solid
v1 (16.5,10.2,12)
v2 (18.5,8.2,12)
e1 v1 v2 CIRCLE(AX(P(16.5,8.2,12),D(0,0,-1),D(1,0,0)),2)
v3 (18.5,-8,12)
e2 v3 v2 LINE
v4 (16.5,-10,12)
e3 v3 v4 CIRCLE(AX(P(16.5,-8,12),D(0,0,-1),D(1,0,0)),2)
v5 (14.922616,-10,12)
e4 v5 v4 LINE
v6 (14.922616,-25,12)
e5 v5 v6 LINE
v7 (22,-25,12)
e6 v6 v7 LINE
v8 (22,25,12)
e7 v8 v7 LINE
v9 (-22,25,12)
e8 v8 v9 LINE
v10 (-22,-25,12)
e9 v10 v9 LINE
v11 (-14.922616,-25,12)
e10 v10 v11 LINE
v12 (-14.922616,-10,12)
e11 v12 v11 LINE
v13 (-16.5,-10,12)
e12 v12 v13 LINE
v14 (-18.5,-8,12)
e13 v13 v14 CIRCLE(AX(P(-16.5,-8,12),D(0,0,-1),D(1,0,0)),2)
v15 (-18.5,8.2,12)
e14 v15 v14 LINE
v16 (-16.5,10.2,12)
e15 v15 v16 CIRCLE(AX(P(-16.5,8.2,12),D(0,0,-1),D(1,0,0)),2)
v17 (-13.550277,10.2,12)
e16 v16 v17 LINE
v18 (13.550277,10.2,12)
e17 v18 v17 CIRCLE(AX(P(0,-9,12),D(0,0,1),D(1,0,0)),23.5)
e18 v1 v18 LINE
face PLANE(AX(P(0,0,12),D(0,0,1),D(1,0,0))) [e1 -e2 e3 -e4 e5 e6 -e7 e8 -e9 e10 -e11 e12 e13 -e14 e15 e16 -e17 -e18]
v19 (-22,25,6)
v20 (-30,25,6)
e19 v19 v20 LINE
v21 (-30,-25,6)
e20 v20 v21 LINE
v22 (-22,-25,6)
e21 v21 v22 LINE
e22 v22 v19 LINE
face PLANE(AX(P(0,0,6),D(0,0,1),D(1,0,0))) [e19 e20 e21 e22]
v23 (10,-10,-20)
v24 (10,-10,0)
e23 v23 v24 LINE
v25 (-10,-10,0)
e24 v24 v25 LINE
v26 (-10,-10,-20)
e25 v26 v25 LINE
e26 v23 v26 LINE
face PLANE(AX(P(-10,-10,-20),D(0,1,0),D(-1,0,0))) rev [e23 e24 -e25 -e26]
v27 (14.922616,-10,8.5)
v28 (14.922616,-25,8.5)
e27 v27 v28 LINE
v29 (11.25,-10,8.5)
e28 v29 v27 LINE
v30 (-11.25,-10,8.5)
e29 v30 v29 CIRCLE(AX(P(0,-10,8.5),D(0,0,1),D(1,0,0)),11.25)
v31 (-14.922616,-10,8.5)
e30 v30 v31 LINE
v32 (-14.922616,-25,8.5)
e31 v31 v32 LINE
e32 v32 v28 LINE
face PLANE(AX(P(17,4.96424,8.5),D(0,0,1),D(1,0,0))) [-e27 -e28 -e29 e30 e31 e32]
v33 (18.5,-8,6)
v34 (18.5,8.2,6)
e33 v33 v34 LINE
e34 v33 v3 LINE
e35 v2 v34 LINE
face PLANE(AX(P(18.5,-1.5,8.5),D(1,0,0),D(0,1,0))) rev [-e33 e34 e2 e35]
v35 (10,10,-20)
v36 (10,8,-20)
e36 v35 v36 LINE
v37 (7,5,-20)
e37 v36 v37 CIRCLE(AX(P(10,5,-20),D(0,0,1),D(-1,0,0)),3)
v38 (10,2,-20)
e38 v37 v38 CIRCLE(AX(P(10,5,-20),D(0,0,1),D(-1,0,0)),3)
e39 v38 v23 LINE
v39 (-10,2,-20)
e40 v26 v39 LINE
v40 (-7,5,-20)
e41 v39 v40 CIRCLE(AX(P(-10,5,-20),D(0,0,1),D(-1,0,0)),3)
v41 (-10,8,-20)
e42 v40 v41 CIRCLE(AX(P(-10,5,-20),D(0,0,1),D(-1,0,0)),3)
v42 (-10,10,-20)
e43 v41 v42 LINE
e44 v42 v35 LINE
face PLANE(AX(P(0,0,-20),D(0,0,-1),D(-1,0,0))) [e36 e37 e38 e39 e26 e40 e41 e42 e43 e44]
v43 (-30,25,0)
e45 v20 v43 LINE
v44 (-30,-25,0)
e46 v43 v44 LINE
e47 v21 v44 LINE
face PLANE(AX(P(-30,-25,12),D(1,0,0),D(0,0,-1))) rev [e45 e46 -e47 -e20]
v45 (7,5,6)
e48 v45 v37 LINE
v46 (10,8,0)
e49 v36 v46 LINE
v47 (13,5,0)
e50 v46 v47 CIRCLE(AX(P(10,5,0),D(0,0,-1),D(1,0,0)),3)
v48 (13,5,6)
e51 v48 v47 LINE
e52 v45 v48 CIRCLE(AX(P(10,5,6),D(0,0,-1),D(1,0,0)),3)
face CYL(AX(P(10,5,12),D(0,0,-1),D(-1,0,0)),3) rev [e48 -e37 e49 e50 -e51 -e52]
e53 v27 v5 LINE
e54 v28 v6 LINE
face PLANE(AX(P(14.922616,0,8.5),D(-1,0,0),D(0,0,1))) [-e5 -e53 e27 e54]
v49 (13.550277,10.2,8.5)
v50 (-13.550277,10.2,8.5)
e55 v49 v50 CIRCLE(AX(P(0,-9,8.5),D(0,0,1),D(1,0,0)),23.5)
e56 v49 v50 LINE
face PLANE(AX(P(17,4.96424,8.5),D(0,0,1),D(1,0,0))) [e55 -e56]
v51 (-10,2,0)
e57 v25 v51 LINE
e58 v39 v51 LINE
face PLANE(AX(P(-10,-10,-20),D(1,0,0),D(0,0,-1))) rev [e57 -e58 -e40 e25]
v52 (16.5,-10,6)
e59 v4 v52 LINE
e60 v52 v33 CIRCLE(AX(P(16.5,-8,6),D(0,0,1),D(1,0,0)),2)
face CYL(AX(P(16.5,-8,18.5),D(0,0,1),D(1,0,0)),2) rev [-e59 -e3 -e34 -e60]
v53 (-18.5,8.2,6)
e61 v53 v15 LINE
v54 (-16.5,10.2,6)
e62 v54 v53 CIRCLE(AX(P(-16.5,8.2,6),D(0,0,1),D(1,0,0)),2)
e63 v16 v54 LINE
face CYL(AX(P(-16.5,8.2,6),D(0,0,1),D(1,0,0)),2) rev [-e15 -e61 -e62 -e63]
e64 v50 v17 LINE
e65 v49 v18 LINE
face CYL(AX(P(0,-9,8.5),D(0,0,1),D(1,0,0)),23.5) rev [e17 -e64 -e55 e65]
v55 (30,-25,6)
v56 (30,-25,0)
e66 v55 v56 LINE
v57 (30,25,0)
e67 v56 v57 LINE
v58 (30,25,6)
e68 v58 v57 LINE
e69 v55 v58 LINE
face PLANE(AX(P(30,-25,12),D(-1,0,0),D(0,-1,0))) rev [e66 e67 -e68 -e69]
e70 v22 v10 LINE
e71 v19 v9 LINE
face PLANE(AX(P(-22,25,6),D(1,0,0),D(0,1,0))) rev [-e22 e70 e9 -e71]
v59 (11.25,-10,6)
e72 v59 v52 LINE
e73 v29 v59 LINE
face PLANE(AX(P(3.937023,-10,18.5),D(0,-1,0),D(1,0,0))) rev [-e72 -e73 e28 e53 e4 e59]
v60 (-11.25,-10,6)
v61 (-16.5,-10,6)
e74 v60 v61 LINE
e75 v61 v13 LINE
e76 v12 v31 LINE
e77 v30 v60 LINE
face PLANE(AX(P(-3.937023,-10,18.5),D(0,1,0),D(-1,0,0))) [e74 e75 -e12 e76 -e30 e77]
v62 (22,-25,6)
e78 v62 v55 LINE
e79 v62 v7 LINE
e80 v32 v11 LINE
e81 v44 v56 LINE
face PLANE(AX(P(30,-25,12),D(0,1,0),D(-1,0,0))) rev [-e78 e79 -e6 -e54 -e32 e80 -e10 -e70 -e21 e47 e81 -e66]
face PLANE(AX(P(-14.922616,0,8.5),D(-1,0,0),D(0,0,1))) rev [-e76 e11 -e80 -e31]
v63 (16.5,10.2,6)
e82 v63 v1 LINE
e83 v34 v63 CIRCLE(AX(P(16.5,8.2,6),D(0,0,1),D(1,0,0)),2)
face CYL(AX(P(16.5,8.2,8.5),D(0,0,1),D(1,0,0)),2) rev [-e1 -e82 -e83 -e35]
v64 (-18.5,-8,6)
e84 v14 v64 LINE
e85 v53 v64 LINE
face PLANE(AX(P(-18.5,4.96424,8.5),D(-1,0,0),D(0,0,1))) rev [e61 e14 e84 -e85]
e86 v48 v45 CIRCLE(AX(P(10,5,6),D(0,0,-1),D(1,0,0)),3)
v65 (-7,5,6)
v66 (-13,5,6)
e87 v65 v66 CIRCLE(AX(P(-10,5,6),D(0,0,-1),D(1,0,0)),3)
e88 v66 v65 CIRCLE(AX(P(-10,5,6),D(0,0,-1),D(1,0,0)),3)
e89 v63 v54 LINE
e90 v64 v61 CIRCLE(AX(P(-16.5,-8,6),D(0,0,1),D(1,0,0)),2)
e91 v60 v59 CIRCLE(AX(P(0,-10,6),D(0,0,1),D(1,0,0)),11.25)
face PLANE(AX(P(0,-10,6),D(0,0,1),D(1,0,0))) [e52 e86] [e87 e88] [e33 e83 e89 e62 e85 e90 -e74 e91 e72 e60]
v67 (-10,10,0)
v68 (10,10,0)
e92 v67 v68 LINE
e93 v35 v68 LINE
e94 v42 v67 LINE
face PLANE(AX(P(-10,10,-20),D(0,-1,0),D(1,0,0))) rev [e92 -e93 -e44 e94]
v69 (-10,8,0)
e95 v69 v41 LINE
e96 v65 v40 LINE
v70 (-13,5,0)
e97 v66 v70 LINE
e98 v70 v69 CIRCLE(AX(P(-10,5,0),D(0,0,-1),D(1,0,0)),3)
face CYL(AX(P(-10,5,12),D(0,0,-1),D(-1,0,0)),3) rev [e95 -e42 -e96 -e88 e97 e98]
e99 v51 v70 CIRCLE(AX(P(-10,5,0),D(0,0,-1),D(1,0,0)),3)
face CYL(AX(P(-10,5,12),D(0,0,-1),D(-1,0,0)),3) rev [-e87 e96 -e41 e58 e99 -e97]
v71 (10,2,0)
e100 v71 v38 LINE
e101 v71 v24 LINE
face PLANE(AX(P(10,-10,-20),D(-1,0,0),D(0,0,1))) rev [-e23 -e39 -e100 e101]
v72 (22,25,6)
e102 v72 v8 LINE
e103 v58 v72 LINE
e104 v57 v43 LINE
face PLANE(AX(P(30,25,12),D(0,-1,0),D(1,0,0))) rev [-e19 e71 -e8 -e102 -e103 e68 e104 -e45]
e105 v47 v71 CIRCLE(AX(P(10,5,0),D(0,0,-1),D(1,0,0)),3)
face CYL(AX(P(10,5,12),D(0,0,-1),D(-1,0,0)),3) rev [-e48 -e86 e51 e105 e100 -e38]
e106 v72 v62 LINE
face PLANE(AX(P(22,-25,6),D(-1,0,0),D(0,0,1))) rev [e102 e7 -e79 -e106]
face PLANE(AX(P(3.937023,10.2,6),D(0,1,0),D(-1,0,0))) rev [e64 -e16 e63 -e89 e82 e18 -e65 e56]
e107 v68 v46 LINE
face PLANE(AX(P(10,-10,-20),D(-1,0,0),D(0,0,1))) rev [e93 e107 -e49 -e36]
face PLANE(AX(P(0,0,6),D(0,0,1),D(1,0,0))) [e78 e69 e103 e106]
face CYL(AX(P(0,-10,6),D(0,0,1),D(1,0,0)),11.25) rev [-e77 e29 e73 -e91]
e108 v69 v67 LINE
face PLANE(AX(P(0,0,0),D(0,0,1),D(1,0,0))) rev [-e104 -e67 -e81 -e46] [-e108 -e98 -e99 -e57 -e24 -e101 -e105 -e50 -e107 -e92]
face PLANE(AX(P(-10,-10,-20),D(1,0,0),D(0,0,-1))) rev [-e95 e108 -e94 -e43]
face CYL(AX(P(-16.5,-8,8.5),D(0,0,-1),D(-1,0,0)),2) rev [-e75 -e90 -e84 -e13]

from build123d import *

# Parameters (mm, degrees)
SKETCH_1_W                      = 60
SKETCH_1_H                      = 50
EXTRUDE_1_DEPTH                 = 12
SKETCH_2_W                      = 20
SKETCH_2_H                      = 20
EXTRUDE_2_DEPTH                 = 20
SKETCH_3_R                      = 10.5
CUT_EXTRUDE_1_DEPTH             = 6
CUT_EXTRUDE_2_DEPTH             = 3.5
CUT_EXTRUDE_3_DEPTH             = 3.5
CUT_EXTRUDE_4_DEPTH             = 2.5
CUT_EXTRUDE_5_REACH             = 48.915
SKETCH_8_R                      = 3
CUT_EXTRUDE_5_DIRECTION_2_DEPTH = 47.914816423
SKETCH_9_W                      = 8
SKETCH_9_H                      = 50
CUT_EXTRUDE_6_DEPTH             = 6
CUT_EXTRUDE_START               = -2.5
SKETCH_10_W                     = 14.56297708
SKETCH_10_H                     = 20.2
CUT_EXTRUDE_7_DEPTH             = 12.5
FILLET_1_R                      = 2


with BuildPart() as part:
    # 草图1 → 凸台-拉伸1 (new body)
    with BuildSketch(Plane.XY):
        Rectangle(SKETCH_1_W, SKETCH_1_H)
    extrude(amount=EXTRUDE_1_DEPTH)

    # 草图2 → 凸台-拉伸2 (add)
    with BuildSketch(Plane(origin=(0, 0, 0), x_dir=(-1, 0, 0), z_dir=(0, 0, -1))):
        Rectangle(SKETCH_2_W, SKETCH_2_H)
    extrude(amount=EXTRUDE_2_DEPTH)

    # 草图3 → 切除-拉伸1 (cut)
    with BuildSketch(Plane.XY.offset(12)):
        with Locations((0, -10)):
            Circle(SKETCH_3_R)
    extrude(amount=-CUT_EXTRUDE_1_DEPTH, mode=Mode.SUBTRACT)

    # 草图5 → 切除-拉伸2 (cut)
    with BuildSketch(Plane.XY.offset(12)):
        with BuildLine():
            Line((-18.5, 4.964240044), (-18.5, -1.5))
            ThreePointArc((-18.5, -1.5), (-18.060660172, -2.560660172), (-17, -3))
            Line((-17, -3), (-12.845232579, -3))
            ThreePointArc((-12.845232579, -3), (-12.301125391, -2.897836674), (-11.83113527, -2.605263158))
            ThreePointArc((-11.83113527, -2.605263158), (0, 2), (11.83113527, -2.605263158))
            ThreePointArc((11.83113527, -2.605263158), (12.301125391, -2.897836674), (12.845232579, -3))
            Line((12.845232579, -3), (17, -3))
            ThreePointArc((17, -3), (18.060660172, -2.560660172), (18.5, -1.5))
            Line((18.5, -1.5), (18.5, 4.964240044))
            ThreePointArc((18.5, 4.964240044), (18.412203308, 5.469889941), (18.159090909, 5.916347319))
            ThreePointArc((18.159090909, 5.916347319), (0, 14.5), (-18.159090909, 5.916347319))
            ThreePointArc((-18.159090909, 5.916347319), (-18.412203308, 5.469889941), (-18.5, 4.964240044))
        make_face()
    extrude(amount=-CUT_EXTRUDE_2_DEPTH, mode=Mode.SUBTRACT)

    # 草图6 → 切除-拉伸3 (cut)
    with BuildSketch(Plane.XY.offset(12)):
        with BuildLine():
            Line((-13.389251051, -3), (-14.922616289, -3))
            Line((-14.922616289, -3), (-14.922616289, -25))
            Line((-14.922616289, -25), (14.922616289, -25))
            Line((14.922616289, -25), (14.922616289, -3))
            Line((14.922616289, -3), (13.389251051, -3))
            Line((13.389251051, -3), (13.389251051, -8.470382759))
            Line((13.389251051, -8.470382759), (10.387986864, -8.470382759))
            ThreePointArc((10.387986864, -8.470382759), (10.471959274, -9.233143454), (10.5, -10))
            ThreePointArc((10.5, -10), (-0.766856546, -20.471959274), (-10.387986864, -8.470382759))
            Line((-10.387986864, -8.470382759), (-13.389251051, -8.470382759))
            Line((-13.389251051, -8.470382759), (-13.389251051, -3))
        make_face()
        with BuildLine():
            Line((7.826237921, -3), (-7.826237921, -3))
            ThreePointArc((-7.826237921, -3), (-9.508983543, -5.546997419), (-10.387986864, -8.470382759))
            Line((-10.387986864, -8.470382759), (10.387986864, -8.470382759))
            ThreePointArc((10.387986864, -8.470382759), (9.508983543, -5.546997419), (7.826237921, -3))
        make_face()
        with BuildLine():
            ThreePointArc((7.826237921, -3), (0, 0.5), (-7.826237921, -3))
            Line((-7.826237921, -3), (7.826237921, -3))
        make_face()
        with BuildLine():
            ThreePointArc((-11.83113527, -2.605263158), (-12.301125391, -2.897836674), (-12.845232579, -3))
            Line((-12.845232579, -3), (-7.826237921, -3))
            ThreePointArc((-7.826237921, -3), (0, 0.5), (7.826237921, -3))
            Line((7.826237921, -3), (12.845232579, -3))
            ThreePointArc((12.845232579, -3), (12.301125391, -2.897836674), (11.83113527, -2.605263158))
            ThreePointArc((11.83113527, -2.605263158), (0, 2), (-11.83113527, -2.605263158))
        make_face()
        with BuildLine():
            Line((-12.845232579, -3), (-13.389251051, -3))
            Line((-13.389251051, -3), (-13.389251051, -8.470382759))
            Line((-13.389251051, -8.470382759), (-10.387986864, -8.470382759))
            ThreePointArc((-10.387986864, -8.470382759), (-9.508983543, -5.546997419), (-7.826237921, -3))
            Line((-7.826237921, -3), (-12.845232579, -3))
        make_face()
        with BuildLine():
            Line((12.845232579, -3), (7.826237921, -3))
            ThreePointArc((7.826237921, -3), (9.508983543, -5.546997419), (10.387986864, -8.470382759))
            Line((10.387986864, -8.470382759), (13.389251051, -8.470382759))
            Line((13.389251051, -8.470382759), (13.389251051, -3))
            Line((13.389251051, -3), (12.845232579, -3))
        make_face()
    extrude(amount=-CUT_EXTRUDE_3_DEPTH, mode=Mode.SUBTRACT)

    # 草图7 → 切除-拉伸4 (cut)
    with BuildSketch(Plane.XY.offset(8.5)):
        with BuildLine():
            Line((-18.5, 0.049973913), (-18.5, 0))
            ThreePointArc((-18.5, 0), (-18.060660172, -1.060660172), (-17, -1.5))
            Line((-17, -1.5), (-12.371843032, -1.5))
            ThreePointArc((-12.371843032, -1.5), (-10.253202816, -2.672836244), (-10.122417026, -5.090909091))
            ThreePointArc((-10.122417026, -5.090909091), (0, -21.25), (10.122417026, -5.090909091))
            ThreePointArc((10.122417026, -5.090909091), (10.253202816, -2.672836244), (12.371843032, -1.5))
            Line((12.371843032, -1.5), (17, -1.5))
            ThreePointArc((17, -1.5), (18.060660172, -1.060660172), (18.5, 0))
            Line((18.5, 0), (18.5, 0.049973913))
            ThreePointArc((18.5, 0.049973913), (18.340320328, 0.929121661), (17.881679389, 1.69596379))
            ThreePointArc((17.881679389, 1.69596379), (12.348306903, 6.580233667), (5.752265423, 9.891810345))
            ThreePointArc((5.752265423, 9.891810345), (4.857632257, 10.122405227), (3.93702292, 10.2))
            Line((3.93702292, 10.2), (-3.93702292, 10.2))
            ThreePointArc((-3.93702292, 10.2), (-4.857632257, 10.122405227), (-5.752265423, 9.891810345))
            ThreePointArc((-5.752265423, 9.891810345), (-12.348306903, 6.580233667), (-17.881679389, 1.69596379))
            ThreePointArc((-17.881679389, 1.69596379), (-18.340320328, 0.929121661), (-18.5, 0.049973913))
        make_face()
    extrude(amount=-CUT_EXTRUDE_4_DEPTH, mode=Mode.SUBTRACT)

    # 草图8 → 切除-拉伸5 (cut, up to next)
    with BuildSketch(Plane.XY.offset(6), mode=Mode.PRIVATE) as cut_extrude_5_sk1:
        with Locations(Location((-10, 5, 0), (0, 0, 153.145976086))):
            Circle(SKETCH_8_R)
    cut_extrude_5_tool1 = extrude(cut_extrude_5_sk1.sketch, amount=-CUT_EXTRUDE_5_REACH, mode=Mode.PRIVATE) & part.part
    # 草图8 → 切除-拉伸5 (cut, up to next)
    with BuildSketch(Plane.XY.offset(6), mode=Mode.PRIVATE) as cut_extrude_5_sk2:
        with Locations(Location((10, 5, 0), (0, 0, 90))):
            Circle(SKETCH_8_R)
    cut_extrude_5_tool2 = extrude(cut_extrude_5_sk2.sketch, amount=-CUT_EXTRUDE_5_REACH, mode=Mode.PRIVATE) & part.part
    add(cut_extrude_5_tool1.solids().sort_by_distance((-10, 5, 6))[0], mode=Mode.SUBTRACT)
    add(cut_extrude_5_tool2.solids().sort_by_distance((10, 5, 6))[0], mode=Mode.SUBTRACT)

    # 草图8 → 切除-拉伸5 direction 2 (cut)
    with BuildSketch(Plane.XY.offset(6)):
        with Locations(Location((-10, 5, 0), (0, 0, 153.145976086))):
            Circle(SKETCH_8_R)
        with Locations(Location((10, 5, 0), (0, 0, 90))):
            Circle(SKETCH_8_R)
    extrude(amount=CUT_EXTRUDE_5_DIRECTION_2_DEPTH, mode=Mode.SUBTRACT)

    # 草图9 → 切除-拉伸6 (cut)
    with BuildSketch(Plane.XY.offset(12)):
        with Locations((-26, 0)):
            Rectangle(SKETCH_9_W, SKETCH_9_H)
        with Locations((26, 0)):
            Rectangle(SKETCH_9_W, SKETCH_9_H)
    extrude(amount=-CUT_EXTRUDE_6_DEPTH, mode=Mode.SUBTRACT)

    # 草图10 → 切除-拉伸7 (cut)
    with BuildSketch(Plane.XY.offset(8.5).offset(CUT_EXTRUDE_START)):
        with Locations((-11.21851146, 0.1)):
            Rectangle(SKETCH_10_W, SKETCH_10_H)
    cut_extrude_7 = extrude(amount=CUT_EXTRUDE_7_DEPTH, mode=Mode.SUBTRACT)

    # 镜向2: 切除-拉伸7 across plane
    add(cut_extrude_7.mirror(Plane(origin=(0, 0, 0), x_dir=(0, 0, 1), z_dir=(1, 0, 0))), mode=Mode.SUBTRACT)

    # 圆角1
    fillet_1_edges = [part.edges().sort_by_distance(p)[0] for p in [
        (-18.5, 10.2, 9),
        (-18.5, -10, 9),
        (18.5, -10, 9),
        (18.5, 10.2, 9),
    ]]
    fillet(fillet_1_edges, radius=FILLET_1_R)


solid = part.part
